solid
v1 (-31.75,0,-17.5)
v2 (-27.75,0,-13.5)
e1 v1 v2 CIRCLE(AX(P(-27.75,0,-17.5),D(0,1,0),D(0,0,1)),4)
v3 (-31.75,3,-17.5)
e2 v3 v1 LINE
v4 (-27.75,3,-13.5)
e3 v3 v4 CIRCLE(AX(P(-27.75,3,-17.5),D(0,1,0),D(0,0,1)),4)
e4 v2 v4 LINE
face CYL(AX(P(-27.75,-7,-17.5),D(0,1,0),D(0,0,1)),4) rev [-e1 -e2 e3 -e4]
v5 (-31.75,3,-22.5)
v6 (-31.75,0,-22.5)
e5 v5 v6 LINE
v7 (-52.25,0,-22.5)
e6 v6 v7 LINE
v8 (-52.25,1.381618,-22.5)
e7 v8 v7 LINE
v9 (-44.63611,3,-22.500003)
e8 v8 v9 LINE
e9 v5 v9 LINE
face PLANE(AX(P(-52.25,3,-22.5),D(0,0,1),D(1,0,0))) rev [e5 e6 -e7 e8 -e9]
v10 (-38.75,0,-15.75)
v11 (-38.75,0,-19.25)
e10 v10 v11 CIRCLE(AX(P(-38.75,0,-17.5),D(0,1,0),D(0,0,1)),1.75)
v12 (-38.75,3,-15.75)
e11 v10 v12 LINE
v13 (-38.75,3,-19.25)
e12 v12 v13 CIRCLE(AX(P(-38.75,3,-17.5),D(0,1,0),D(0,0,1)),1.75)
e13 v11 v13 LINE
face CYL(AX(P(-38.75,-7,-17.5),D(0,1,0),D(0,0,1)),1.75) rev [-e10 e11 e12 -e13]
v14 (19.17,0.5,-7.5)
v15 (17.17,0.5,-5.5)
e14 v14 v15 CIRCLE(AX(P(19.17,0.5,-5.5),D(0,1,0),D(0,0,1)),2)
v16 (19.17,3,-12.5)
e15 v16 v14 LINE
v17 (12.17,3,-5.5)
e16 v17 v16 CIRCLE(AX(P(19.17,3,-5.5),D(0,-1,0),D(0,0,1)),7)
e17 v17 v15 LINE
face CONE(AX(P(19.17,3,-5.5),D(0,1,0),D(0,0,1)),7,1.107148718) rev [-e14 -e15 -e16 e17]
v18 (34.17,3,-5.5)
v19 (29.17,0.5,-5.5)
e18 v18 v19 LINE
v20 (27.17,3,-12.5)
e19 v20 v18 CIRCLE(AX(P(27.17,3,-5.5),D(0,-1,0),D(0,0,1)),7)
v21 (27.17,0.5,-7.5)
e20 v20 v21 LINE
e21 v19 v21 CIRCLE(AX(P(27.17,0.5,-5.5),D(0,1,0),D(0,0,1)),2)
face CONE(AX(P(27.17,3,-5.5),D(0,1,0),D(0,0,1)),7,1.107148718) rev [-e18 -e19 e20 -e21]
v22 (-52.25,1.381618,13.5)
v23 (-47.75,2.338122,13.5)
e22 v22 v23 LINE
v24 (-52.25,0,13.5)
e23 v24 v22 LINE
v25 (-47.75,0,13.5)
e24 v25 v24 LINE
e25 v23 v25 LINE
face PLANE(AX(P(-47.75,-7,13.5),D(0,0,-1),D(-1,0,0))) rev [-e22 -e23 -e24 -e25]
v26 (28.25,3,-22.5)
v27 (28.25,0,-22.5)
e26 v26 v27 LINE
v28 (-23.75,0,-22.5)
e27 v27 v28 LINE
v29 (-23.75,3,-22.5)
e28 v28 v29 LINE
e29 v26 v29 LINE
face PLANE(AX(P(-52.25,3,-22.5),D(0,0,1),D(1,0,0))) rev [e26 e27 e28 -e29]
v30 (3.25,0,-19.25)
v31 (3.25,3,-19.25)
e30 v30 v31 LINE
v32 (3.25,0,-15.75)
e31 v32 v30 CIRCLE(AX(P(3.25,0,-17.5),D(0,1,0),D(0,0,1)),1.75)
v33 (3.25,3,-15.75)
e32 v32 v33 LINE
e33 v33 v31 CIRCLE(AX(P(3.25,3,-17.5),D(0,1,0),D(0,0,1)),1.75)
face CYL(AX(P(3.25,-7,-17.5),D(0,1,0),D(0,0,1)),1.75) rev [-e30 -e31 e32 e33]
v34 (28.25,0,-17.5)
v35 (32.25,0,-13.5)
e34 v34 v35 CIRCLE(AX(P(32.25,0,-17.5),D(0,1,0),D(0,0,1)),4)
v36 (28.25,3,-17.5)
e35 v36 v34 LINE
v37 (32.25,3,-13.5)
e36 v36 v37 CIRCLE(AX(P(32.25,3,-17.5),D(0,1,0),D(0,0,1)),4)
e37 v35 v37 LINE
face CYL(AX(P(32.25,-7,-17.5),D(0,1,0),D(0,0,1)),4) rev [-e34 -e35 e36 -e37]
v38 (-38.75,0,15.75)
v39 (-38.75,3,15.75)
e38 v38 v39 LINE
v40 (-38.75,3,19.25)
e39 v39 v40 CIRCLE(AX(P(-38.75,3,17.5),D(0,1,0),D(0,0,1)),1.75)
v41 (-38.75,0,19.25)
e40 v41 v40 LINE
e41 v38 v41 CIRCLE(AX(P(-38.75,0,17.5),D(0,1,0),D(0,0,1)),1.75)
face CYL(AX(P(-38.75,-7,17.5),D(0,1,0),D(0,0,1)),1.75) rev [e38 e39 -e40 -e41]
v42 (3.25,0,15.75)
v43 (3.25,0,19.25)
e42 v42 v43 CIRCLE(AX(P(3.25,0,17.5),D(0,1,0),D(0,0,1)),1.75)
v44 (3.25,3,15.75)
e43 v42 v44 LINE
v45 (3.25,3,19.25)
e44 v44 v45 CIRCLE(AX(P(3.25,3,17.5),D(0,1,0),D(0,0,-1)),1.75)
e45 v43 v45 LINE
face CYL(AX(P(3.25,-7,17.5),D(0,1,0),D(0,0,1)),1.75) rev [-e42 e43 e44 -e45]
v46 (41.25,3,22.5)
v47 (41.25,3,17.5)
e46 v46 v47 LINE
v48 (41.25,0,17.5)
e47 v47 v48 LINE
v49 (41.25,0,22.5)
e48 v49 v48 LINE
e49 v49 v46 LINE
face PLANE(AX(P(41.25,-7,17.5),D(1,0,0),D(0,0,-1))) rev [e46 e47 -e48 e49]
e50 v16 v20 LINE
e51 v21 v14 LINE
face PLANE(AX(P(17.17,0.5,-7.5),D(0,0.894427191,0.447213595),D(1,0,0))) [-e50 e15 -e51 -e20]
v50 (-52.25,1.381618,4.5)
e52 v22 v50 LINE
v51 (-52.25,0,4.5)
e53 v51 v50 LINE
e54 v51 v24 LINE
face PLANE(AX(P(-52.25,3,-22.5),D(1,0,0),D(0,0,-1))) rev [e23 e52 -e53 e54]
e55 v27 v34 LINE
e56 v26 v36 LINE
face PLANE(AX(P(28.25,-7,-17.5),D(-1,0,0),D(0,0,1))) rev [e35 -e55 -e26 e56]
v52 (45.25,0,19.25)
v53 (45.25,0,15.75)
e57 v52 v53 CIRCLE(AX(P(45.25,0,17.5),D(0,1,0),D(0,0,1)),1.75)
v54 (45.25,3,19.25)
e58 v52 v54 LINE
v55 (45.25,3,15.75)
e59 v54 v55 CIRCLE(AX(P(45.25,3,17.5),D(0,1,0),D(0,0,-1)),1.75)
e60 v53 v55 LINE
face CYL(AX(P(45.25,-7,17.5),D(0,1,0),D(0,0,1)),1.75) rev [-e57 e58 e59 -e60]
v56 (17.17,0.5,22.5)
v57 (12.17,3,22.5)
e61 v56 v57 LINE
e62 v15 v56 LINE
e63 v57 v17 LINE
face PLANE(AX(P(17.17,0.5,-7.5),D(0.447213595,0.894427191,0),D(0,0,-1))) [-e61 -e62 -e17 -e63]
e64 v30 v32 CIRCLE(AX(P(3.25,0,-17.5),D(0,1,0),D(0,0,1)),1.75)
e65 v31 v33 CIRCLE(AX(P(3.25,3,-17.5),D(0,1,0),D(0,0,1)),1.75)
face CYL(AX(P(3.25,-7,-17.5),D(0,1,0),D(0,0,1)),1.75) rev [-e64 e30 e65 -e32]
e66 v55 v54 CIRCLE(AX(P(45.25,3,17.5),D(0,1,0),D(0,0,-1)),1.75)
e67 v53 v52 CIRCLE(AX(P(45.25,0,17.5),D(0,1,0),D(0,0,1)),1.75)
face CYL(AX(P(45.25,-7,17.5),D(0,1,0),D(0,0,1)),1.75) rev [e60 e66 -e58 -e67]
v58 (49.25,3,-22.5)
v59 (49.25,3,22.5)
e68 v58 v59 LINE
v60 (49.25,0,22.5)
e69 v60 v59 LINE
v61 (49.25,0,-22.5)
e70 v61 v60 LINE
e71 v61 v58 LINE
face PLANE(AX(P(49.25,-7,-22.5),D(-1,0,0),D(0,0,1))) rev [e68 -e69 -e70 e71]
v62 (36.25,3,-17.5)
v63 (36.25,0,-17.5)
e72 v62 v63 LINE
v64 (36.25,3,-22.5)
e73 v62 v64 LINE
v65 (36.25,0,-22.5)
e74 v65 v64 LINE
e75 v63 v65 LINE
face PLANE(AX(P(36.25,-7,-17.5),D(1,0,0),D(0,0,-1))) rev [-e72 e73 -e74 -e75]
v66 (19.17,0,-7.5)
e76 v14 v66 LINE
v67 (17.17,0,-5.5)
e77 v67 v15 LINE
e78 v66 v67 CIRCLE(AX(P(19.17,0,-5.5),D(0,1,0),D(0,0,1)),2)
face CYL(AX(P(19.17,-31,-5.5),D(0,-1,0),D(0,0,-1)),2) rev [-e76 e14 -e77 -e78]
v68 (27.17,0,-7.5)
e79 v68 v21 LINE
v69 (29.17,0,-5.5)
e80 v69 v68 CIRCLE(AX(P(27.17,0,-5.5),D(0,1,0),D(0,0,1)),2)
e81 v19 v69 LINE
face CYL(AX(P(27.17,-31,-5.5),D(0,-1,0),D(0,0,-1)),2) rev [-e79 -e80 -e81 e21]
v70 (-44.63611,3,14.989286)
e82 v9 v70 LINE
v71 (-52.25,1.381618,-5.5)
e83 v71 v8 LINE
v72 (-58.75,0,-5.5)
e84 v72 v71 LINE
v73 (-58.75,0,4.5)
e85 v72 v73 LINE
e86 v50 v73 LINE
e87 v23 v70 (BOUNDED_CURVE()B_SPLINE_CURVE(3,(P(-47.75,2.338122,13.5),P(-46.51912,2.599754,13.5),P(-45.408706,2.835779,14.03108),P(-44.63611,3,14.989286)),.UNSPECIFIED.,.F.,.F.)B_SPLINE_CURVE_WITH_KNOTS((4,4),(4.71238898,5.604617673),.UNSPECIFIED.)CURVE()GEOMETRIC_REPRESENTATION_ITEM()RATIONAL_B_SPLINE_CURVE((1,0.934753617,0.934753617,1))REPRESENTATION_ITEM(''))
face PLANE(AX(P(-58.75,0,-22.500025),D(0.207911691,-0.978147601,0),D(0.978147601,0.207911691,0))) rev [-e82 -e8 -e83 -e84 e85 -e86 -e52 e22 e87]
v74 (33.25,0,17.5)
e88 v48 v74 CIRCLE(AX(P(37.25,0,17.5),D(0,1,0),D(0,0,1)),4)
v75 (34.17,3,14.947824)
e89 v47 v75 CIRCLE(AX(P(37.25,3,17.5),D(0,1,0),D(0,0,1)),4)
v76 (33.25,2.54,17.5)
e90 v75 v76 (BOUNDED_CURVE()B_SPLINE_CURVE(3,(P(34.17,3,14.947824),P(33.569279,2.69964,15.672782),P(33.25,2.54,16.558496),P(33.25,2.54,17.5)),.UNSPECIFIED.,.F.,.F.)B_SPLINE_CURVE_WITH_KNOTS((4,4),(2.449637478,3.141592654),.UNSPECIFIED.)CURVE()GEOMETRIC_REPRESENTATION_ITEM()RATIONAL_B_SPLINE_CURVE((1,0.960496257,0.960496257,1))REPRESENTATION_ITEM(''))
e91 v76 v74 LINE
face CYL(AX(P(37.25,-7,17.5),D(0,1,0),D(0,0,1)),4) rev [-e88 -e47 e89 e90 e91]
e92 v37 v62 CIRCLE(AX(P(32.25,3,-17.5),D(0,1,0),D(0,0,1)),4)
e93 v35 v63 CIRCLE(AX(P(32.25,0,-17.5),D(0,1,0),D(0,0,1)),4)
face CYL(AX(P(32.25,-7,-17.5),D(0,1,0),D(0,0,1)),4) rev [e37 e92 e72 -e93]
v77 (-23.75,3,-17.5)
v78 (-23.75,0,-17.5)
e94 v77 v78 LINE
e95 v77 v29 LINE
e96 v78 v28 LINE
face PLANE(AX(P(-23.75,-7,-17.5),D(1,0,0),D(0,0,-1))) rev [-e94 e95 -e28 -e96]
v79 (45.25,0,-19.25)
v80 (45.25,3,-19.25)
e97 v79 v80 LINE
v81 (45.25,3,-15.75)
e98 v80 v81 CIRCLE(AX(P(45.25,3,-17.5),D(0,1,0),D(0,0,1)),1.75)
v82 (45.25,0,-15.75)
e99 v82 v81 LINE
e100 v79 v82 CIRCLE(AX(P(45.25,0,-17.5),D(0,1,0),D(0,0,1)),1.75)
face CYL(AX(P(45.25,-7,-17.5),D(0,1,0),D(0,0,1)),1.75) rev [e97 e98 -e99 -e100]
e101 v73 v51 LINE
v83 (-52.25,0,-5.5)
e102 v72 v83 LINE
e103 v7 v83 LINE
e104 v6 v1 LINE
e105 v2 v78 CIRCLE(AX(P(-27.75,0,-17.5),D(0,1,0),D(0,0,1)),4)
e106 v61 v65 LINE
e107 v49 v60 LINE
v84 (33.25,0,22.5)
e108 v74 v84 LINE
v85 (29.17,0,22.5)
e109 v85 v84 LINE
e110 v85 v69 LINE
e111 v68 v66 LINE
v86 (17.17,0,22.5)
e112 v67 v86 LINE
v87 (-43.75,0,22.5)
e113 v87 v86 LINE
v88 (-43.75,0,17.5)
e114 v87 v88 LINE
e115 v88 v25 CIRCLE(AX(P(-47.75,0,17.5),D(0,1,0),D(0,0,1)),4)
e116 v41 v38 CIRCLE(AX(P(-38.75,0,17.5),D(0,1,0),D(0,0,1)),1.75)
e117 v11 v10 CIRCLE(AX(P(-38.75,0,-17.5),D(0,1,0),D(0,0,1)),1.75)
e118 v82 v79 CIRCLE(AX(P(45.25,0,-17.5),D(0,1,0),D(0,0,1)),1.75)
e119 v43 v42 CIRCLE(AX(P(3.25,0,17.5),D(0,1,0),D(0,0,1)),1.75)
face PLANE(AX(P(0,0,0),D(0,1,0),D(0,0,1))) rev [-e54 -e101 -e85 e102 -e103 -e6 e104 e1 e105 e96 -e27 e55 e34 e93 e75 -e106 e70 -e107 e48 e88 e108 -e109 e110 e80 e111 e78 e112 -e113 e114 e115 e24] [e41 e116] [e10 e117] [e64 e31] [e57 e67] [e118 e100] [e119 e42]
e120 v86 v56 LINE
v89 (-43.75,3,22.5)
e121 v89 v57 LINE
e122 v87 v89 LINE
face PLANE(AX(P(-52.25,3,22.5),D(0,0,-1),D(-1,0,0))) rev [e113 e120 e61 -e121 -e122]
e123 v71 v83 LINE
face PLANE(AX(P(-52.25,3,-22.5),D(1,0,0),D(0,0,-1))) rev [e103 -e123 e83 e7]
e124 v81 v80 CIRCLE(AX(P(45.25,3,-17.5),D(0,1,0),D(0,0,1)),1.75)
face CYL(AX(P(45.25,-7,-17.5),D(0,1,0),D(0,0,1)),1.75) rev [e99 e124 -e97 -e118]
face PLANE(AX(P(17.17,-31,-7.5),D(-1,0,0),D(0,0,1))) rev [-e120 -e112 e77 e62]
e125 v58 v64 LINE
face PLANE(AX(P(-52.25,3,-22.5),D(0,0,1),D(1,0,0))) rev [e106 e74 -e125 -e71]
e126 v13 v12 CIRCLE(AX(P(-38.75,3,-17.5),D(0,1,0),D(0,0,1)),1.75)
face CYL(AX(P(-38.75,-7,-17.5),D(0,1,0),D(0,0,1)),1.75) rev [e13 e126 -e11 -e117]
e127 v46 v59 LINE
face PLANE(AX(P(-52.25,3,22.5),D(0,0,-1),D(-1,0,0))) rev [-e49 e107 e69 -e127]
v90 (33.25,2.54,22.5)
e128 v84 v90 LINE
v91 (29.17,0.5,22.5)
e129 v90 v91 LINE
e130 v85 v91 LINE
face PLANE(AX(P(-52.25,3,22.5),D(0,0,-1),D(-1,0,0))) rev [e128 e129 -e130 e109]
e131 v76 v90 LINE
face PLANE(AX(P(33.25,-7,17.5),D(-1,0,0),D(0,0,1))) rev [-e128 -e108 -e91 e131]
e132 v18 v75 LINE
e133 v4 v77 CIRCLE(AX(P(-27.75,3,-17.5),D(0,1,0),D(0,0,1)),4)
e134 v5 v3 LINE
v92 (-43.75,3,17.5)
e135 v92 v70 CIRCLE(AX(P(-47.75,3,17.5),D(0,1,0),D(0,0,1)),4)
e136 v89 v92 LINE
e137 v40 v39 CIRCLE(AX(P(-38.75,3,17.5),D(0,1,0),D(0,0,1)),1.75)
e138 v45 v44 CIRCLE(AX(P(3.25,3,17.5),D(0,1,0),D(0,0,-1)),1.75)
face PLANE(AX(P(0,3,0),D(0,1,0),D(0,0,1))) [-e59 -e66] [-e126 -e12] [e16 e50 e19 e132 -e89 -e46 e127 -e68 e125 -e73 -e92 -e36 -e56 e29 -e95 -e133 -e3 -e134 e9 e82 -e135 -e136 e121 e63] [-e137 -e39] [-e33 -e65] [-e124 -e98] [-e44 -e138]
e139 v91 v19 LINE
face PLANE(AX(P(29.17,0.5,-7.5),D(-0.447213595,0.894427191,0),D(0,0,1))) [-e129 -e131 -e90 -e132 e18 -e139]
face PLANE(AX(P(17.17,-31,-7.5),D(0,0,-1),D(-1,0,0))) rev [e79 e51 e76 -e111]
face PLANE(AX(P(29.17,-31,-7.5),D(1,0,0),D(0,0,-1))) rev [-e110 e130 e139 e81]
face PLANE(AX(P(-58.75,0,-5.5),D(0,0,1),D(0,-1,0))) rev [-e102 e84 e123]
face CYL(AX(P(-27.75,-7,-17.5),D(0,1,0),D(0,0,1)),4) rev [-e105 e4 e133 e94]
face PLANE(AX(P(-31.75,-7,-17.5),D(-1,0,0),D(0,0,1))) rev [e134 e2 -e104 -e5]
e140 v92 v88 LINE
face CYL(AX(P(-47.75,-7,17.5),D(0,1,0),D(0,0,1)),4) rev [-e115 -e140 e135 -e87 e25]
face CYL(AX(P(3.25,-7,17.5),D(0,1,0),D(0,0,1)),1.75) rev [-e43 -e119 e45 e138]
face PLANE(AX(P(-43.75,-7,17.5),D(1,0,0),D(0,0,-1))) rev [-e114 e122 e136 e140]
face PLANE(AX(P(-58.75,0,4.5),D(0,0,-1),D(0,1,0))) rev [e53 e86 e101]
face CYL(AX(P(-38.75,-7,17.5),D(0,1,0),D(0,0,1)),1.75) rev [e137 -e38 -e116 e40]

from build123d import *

# Parameters (mm, degrees)
SKETCH1_W           = 104.5
SKETCH1_H           = 45
BOSS_EXTRUDE1_DEPTH = 3
SKETCH2_W           = 12
SKETCH2_H           = 30
CUT_EXTRUDE1_DEPTH  = 34
SKETCH3_W           = 3
SKETCH3_H           = 45
CUT_EXTRUDE2_DEPTH  = 10
SKETCH4_R           = 1.75
CUT_EXTRUDE3_DEPTH  = 10
SKETCH5_W           = 10
SKETCH5_H           = 3
BOSS_EXTRUDE2_DEPTH = 6.5
CUT_EXTRUDE4_DEPTH  = 75.064583304
SKETCH7_R           = 4
CUT_EXTRUDE5_DEPTH  = 10
SKETCH8_W           = 8
SKETCH8_H           = 8.668176015
CUT_EXTRUDE6_DEPTH  = 10
FILLET1_R           = 2
CHAMFER2_SIZE       = 5
CHAMFER2_SIZE2      = 2.5


with BuildPart() as part:
    # Sketch1 → Boss-Extrude1 (new body)
    with BuildSketch(Plane(origin=(0, 0, 0), x_dir=(1, 0, 0), z_dir=(0, 1, 0))):
        Rectangle(SKETCH1_W, SKETCH1_H)
    extrude(amount=BOSS_EXTRUDE1_DEPTH)

    # Sketch2 → Cut-Extrude1 (cut)
    with BuildSketch(Plane(origin=(0, 3, 0), x_dir=(1, 0, 0), z_dir=(0, 1, 0))):
        with Locations((23.17, -7.5)):
            Rectangle(SKETCH2_W, SKETCH2_H)
    extrude(amount=-CUT_EXTRUDE1_DEPTH, mode=Mode.SUBTRACT)

    # Sketch3 → Cut-Extrude2 (cut)
    with BuildSketch(Plane(origin=(0, 3, 0), x_dir=(1, 0, 0), z_dir=(0, 1, 0))):
        with Locations((50.75, 0)):
            Rectangle(SKETCH3_W, SKETCH3_H)
    extrude(amount=-CUT_EXTRUDE2_DEPTH, mode=Mode.SUBTRACT)

    # Sketch4 → Cut-Extrude3 (cut)
    with BuildSketch(Plane(origin=(0, 3, 0), x_dir=(1, 0, 0), z_dir=(0, 1, 0))):
        with Locations(Location((45.25, 17.5, 0), (0, 0, 270))):
            Circle(SKETCH4_R)
        with Locations(Location((45.25, -17.5, 0), (0, 0, 270))):
            Circle(SKETCH4_R)
        with Locations(Location((-38.75, 17.5, 0), (0, 0, 270))):
            Circle(SKETCH4_R)
        with Locations(Location((3.25, 17.5, 0), (0, 0, 270))):
            Circle(SKETCH4_R)
        with Locations(Location((-38.75, -17.5, 0), (0, 0, 270))):
            Circle(SKETCH4_R)
        with Locations(Location((3.25, -17.5, 0), (0, 0, 270))):
            Circle(SKETCH4_R)
    extrude(amount=-CUT_EXTRUDE3_DEPTH, mode=Mode.SUBTRACT)

    # Sketch5 → Boss-Extrude2 (add)
    with BuildSketch(Plane.ZY.offset(52.25)):
        with Locations((-0.5, 1.5)):
            Rectangle(SKETCH5_W, SKETCH5_H)
    extrude(amount=BOSS_EXTRUDE2_DEPTH)

    # Sketch6 → Cut-Extrude4 (cut, through all)
    with BuildSketch(Plane.XY.offset(22.5)):
        Polygon((-58.75, 0), (-44.636109672, 3), (-58.75, 3), align=None)
    extrude(amount=-CUT_EXTRUDE4_DEPTH, mode=Mode.SUBTRACT)

    # Sketch7 → Cut-Extrude5 (cut)
    with BuildSketch(Plane(origin=(0, 3, 0), x_dir=(1, 0, 0), z_dir=(0, 1, 0))):
        with Locations(Location((-27.75, 17.5, 0), (0, 0, 270))):
            Circle(SKETCH7_R)
        with Locations(Location((-47.75, -17.5, 0), (0, 0, 270))):
            Circle(SKETCH7_R)
        with Locations(Location((32.25, 17.5, 0), (0, 0, 270))):
            Circle(SKETCH7_R)
        with Locations(Location((37.25, -17.5, 0), (0, 0, 270))):
            Circle(SKETCH7_R)
    extrude(amount=-CUT_EXTRUDE5_DEPTH, mode=Mode.SUBTRACT)

    # Sketch8 → Cut-Extrude6 (cut)
    with BuildSketch(Plane(origin=(0, 3, 0), x_dir=(1, 0, 0), z_dir=(0, 1, 0))):
        with Locations((-27.75, 21.834088008)):
            Rectangle(SKETCH8_W, SKETCH8_H)
        with Locations((32.25, 21.834088008)):
            Rectangle(SKETCH8_W, SKETCH8_H)
        with BuildLine():
            Line((41.25, -17.5), (41.25, -22.5))
            Line((41.25, -22.5), (33.25, -22.5))
            Line((33.25, -22.5), (33.25, -17.5))
            ThreePointArc((33.25, -17.5), (37.25, -13.5), (41.25, -17.5))
        make_face()
        with BuildLine():
            Line((-43.75, -17.5), (-43.75, -22.5))
            Line((-43.75, -22.5), (-52.25, -22.5))
            Line((-52.25, -22.5), (-52.25, -13.5))
            Line((-52.25, -13.5), (-47.75, -13.5))
            ThreePointArc((-47.75, -13.5), (-44.921572875, -14.671572875), (-43.75, -17.5))
        make_face()
    extrude(amount=-CUT_EXTRUDE6_DEPTH, mode=Mode.SUBTRACT)

    # Fillet1
    fillet1_edges = [part.edges().sort_by_distance(p)[0] for p in [
        (29.17, 1.5, -7.5),
        (17.17, 1.5, -7.5),
    ]]
    fillet(fillet1_edges, radius=FILLET1_R)

    # Chamfer2
    chamfer2_edges = [part.edges().sort_by_distance(p)[0] for p in [
        (29.17, 3, 8.5),
        (28.584213562, 3, -6.914213562),
        (23.17, 3, -7.5),
        (17.755786438, 3, -6.914213562),
        (17.17, 3, 8.5),
    ]]
    chamfer2_side = [part.faces().sort_by_distance(p)[0] for p in [
        (-0.332275855, 3, -0.451474159),
    ]]
    chamfer(chamfer2_edges, length=CHAMFER2_SIZE, length2=CHAMFER2_SIZE2, reference=chamfer2_side[0])


solid = part.part
